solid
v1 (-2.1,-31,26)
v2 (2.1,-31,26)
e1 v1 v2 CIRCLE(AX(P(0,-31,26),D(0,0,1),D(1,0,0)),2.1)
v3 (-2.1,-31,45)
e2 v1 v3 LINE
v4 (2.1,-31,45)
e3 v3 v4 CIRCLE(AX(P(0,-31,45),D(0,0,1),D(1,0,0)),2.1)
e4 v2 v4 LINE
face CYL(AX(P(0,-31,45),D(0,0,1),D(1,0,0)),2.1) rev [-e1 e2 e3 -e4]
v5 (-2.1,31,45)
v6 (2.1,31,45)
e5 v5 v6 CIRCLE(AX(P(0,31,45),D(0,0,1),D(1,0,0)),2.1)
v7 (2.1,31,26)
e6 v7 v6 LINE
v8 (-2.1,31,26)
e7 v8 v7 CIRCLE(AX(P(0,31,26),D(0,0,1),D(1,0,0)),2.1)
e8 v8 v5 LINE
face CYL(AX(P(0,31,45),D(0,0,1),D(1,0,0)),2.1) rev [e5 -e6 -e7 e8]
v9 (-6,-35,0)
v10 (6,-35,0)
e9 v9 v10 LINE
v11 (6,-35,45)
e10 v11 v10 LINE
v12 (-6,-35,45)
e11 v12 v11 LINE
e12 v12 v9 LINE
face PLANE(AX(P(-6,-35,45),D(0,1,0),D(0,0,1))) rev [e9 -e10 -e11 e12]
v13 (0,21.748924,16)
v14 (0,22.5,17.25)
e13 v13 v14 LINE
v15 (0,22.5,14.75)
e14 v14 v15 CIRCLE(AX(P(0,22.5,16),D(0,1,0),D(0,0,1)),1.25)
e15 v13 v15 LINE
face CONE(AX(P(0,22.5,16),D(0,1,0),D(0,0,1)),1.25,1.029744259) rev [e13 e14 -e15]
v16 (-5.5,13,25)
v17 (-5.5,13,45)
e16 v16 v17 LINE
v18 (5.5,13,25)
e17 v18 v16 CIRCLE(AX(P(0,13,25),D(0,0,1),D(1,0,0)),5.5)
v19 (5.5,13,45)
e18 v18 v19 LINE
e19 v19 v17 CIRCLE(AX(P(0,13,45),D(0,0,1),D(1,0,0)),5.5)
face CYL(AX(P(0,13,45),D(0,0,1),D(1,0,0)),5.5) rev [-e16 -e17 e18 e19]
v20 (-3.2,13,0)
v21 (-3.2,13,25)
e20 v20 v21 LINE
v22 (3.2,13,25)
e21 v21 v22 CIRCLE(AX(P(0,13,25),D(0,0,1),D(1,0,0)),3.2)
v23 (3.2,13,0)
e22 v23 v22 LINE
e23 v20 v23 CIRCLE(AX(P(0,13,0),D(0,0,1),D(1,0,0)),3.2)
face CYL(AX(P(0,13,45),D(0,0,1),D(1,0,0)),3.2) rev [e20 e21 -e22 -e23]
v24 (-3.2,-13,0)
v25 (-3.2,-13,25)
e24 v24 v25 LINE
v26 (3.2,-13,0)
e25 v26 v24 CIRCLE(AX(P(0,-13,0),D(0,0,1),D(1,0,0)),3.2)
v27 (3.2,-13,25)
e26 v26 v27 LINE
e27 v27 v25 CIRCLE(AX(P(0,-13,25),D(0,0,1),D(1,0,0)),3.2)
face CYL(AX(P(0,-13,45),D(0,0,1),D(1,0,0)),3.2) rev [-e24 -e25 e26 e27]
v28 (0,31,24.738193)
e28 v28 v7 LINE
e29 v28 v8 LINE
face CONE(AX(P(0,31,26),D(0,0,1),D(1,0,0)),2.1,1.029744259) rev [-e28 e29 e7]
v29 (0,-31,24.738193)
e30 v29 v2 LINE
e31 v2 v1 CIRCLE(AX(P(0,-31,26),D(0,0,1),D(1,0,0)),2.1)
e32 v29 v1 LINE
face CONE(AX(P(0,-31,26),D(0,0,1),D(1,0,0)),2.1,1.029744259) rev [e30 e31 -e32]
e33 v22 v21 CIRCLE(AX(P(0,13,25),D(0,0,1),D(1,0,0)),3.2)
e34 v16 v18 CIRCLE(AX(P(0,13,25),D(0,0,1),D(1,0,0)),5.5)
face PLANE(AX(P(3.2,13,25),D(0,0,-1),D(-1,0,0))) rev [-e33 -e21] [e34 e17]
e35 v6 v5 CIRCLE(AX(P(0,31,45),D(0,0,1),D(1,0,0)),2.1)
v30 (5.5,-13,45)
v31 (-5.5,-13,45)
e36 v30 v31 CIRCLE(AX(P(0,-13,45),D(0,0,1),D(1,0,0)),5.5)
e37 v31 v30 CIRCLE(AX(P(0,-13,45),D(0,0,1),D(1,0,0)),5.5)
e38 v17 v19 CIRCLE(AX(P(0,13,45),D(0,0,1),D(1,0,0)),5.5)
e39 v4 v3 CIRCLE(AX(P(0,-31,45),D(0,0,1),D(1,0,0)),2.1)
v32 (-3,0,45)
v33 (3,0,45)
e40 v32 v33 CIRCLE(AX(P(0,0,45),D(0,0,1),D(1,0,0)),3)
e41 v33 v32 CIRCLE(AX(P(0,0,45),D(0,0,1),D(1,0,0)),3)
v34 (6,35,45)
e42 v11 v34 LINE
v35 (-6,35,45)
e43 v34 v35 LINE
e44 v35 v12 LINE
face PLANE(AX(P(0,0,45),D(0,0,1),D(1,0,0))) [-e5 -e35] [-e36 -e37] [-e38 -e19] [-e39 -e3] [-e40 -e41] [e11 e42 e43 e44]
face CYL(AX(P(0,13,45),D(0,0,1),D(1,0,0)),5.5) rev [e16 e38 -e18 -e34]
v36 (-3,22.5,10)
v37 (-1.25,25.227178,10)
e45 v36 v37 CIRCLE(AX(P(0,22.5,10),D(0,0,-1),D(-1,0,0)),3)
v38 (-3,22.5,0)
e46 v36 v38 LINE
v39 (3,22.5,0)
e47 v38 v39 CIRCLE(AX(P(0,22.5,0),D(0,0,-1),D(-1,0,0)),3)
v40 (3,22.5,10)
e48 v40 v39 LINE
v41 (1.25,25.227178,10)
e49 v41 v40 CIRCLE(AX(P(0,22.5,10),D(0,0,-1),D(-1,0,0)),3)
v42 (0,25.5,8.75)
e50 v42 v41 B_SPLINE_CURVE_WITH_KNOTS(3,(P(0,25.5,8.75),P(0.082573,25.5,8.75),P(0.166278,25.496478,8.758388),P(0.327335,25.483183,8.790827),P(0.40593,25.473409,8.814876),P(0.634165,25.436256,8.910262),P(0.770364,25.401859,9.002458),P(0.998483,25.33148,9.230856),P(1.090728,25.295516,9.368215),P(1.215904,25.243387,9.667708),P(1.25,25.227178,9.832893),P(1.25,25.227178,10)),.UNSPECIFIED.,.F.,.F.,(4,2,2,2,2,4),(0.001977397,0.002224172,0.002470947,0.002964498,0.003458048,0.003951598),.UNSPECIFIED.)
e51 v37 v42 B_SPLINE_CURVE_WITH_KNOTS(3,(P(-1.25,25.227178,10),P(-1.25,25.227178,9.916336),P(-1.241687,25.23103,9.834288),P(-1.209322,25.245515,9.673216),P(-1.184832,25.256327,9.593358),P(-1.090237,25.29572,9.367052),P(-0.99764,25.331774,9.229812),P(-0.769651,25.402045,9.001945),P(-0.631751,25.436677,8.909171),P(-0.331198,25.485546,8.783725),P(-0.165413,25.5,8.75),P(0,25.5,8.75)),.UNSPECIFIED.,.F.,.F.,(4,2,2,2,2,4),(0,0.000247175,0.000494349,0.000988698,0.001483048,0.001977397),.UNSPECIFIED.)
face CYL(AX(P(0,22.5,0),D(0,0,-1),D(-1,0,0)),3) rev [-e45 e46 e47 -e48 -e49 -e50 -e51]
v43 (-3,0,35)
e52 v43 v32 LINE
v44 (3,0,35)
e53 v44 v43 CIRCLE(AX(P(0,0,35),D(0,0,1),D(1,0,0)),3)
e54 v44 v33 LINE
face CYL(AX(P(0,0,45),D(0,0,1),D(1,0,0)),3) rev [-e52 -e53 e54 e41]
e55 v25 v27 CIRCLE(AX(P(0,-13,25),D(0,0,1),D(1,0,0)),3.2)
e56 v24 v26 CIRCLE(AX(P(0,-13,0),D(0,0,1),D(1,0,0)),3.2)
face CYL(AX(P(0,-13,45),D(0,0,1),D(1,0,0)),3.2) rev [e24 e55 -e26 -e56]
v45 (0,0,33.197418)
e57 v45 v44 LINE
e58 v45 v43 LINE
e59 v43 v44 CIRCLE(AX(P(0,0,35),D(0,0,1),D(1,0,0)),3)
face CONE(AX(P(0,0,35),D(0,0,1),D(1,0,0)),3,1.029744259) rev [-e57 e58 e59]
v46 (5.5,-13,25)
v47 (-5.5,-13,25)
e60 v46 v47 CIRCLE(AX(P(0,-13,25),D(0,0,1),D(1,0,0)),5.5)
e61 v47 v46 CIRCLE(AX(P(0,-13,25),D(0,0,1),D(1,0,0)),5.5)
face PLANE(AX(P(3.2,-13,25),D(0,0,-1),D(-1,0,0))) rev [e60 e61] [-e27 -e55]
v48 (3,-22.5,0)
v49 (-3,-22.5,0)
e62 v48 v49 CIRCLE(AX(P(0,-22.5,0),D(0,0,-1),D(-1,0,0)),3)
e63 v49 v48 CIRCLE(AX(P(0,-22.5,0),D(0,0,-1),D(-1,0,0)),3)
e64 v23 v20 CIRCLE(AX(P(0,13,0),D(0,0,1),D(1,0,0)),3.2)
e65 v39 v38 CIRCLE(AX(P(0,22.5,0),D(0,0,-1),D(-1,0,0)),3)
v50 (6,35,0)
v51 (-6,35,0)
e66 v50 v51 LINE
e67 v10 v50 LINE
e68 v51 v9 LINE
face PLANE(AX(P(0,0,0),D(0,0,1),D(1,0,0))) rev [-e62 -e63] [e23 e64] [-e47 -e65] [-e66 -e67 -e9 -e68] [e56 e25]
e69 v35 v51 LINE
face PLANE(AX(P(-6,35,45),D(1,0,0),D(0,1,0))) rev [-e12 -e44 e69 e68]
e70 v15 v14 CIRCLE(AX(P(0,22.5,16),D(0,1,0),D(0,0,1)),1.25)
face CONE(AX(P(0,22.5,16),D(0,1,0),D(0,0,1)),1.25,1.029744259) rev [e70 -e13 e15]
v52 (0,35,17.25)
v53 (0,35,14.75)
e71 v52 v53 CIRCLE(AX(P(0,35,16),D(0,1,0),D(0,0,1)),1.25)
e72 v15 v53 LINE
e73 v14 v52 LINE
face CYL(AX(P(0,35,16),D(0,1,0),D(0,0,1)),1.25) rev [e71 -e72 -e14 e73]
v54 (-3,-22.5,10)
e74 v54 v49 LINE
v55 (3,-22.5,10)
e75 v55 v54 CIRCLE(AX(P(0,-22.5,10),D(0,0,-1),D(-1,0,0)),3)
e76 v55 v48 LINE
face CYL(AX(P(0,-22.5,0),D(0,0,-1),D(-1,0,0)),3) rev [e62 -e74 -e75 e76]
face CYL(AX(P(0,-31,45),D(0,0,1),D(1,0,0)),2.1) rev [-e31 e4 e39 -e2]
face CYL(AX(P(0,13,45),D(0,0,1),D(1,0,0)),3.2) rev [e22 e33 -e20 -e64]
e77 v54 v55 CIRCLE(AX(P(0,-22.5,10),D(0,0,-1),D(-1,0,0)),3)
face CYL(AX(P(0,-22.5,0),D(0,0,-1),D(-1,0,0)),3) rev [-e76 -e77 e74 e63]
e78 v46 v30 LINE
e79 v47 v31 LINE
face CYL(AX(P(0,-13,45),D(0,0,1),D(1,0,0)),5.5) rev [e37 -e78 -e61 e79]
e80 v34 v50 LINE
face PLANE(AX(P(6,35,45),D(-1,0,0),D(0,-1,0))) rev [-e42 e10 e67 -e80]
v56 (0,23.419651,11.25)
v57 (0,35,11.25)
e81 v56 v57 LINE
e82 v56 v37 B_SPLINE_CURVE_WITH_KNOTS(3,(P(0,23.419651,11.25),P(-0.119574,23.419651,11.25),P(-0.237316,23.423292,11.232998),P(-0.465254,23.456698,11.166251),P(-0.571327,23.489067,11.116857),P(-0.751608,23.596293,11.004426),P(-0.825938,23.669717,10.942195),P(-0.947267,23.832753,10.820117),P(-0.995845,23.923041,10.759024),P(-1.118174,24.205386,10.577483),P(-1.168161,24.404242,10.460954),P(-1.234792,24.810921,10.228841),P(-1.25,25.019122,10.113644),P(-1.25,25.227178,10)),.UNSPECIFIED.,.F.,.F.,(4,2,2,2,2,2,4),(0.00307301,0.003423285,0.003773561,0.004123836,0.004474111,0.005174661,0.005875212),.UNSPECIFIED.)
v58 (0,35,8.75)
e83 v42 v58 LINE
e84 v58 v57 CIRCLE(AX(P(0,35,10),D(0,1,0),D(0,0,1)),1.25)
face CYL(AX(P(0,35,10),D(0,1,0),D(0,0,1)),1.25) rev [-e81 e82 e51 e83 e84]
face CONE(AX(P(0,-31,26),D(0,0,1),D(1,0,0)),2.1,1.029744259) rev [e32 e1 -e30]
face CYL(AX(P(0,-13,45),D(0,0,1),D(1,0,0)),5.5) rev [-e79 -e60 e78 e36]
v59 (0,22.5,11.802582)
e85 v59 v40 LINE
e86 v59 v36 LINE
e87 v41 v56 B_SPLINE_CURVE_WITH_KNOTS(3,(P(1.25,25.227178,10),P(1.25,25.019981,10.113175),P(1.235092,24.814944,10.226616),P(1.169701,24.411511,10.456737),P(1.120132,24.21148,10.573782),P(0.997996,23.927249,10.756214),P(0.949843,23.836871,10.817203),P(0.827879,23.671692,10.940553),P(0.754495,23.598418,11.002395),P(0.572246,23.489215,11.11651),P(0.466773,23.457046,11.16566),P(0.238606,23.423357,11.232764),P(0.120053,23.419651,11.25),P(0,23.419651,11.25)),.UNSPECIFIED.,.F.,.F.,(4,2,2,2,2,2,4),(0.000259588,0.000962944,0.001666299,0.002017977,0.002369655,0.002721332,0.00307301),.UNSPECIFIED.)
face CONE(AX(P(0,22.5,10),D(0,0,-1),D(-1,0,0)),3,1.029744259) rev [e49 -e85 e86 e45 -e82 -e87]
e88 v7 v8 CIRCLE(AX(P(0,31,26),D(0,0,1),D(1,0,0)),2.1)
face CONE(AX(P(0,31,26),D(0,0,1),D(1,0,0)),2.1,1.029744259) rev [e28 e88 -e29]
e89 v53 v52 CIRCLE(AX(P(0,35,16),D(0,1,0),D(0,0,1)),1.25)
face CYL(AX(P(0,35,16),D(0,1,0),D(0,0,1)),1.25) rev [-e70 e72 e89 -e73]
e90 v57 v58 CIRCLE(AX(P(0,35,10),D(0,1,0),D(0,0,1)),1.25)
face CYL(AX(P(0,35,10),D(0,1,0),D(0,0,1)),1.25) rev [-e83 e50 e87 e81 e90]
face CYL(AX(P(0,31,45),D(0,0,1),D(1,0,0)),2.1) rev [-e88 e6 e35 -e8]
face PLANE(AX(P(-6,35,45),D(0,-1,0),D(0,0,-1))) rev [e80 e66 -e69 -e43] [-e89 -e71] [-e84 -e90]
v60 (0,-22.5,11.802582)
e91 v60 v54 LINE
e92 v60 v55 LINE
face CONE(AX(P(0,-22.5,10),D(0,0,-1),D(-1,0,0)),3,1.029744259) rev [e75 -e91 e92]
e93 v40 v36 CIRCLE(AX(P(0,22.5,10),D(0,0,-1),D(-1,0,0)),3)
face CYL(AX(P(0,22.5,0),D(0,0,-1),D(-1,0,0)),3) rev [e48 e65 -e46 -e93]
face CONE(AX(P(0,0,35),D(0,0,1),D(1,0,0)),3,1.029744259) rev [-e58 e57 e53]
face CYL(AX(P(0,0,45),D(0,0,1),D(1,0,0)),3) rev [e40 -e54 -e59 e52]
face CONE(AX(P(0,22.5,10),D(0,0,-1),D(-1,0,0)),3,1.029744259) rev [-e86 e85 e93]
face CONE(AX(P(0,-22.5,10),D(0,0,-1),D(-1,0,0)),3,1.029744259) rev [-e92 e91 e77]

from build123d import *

# Parameters (mm, degrees)
SKETCH_13_W               = 12
SKETCH_13_H               = 70
EXTRUDE_1_DEPTH           = 45
HOLE_WIZARD_M3_1_D        = 2.5
HOLE_WIZARD_M3_1_DEPTH    = 12.5
HOLE_WIZARD_M3_1_TIP      = 0.751075774
HOLE_WIZARD_M5_1_D        = 4.2
HOLE_WIZARD_M5_1_DEPTH    = 19
HOLE_WIZARD_M5_1_TIP      = 1.2618073
HOLE_WIZARD_1_D           = 6.4
HOLE_WIZARD_1_CBORE_D     = 11
HOLE_WIZARD_1_CBORE_DEPTH = 20
HOLE_WIZARD_6_0_6_1_D     = 6
HOLE_WIZARD_6_0_6_1_DEPTH = 10
HOLE_WIZARD_6_0_6_1_TIP   = 1.802581857
HOLE_WIZARD_6_0_6_2_D     = 6
HOLE_WIZARD_6_0_6_2_DEPTH = 10
HOLE_WIZARD_6_0_6_2_TIP   = 1.802581857


with BuildPart() as part:
    # 草图13 → 凸台-拉伸1 (new body)
    with BuildSketch(Plane.XY):
        Rectangle(SKETCH_13_W, SKETCH_13_H)
    extrude(amount=EXTRUDE_1_DEPTH)

    # M3 螺纹孔1
    with Locations(Plane(origin=(0, 35, 0), x_dir=(1, 0, 0), z_dir=(0, 1, 0))):
        with Locations((0, -10), (0, -16)):
            Hole(HOLE_WIZARD_M3_1_D / 2, depth=HOLE_WIZARD_M3_1_DEPTH)
            with Locations((0, 0, -(HOLE_WIZARD_M3_1_DEPTH + HOLE_WIZARD_M3_1_TIP / 2))):  # 118° drill point
                Cone(0, HOLE_WIZARD_M3_1_D / 2, HOLE_WIZARD_M3_1_TIP, mode=Mode.SUBTRACT)

    # M5 螺纹孔1
    with Locations(Plane.XY.offset(45)):
        with Locations((0, 31), (0, -31)):
            Hole(HOLE_WIZARD_M5_1_D / 2, depth=HOLE_WIZARD_M5_1_DEPTH)
            with Locations((0, 0, -(HOLE_WIZARD_M5_1_DEPTH + HOLE_WIZARD_M5_1_TIP / 2))):  # 118° drill point
                Cone(0, HOLE_WIZARD_M5_1_D / 2, HOLE_WIZARD_M5_1_TIP, mode=Mode.SUBTRACT)

    # 打孔尺寸(%根据)内六角圆柱头螺钉的类型1 (through all)
    with Locations(Plane.XY.offset(45)):
        with Locations((0, 13), (0, -13)):
            CounterBoreHole(HOLE_WIZARD_1_D / 2, HOLE_WIZARD_1_CBORE_D / 2, HOLE_WIZARD_1_CBORE_DEPTH)

    # Ø6.0 (6) 直径孔1
    with Locations(Plane.XY.offset(45)):
        with Locations((0, 0)):
            Hole(HOLE_WIZARD_6_0_6_1_D / 2, depth=HOLE_WIZARD_6_0_6_1_DEPTH)
            with Locations((0, 0, -(HOLE_WIZARD_6_0_6_1_DEPTH + HOLE_WIZARD_6_0_6_1_TIP / 2))):  # 118° drill point
                Cone(0, HOLE_WIZARD_6_0_6_1_D / 2, HOLE_WIZARD_6_0_6_1_TIP, mode=Mode.SUBTRACT)

    # Ø6.0 (6) 直径孔2
    with Locations(Plane(origin=(0, 0, 0), x_dir=(-1, 0, 0), z_dir=(0, 0, -1))):
        with Locations((0, -22.5), (0, 22.5)):
            Hole(HOLE_WIZARD_6_0_6_2_D / 2, depth=HOLE_WIZARD_6_0_6_2_DEPTH)
            with Locations((0, 0, -(HOLE_WIZARD_6_0_6_2_DEPTH + HOLE_WIZARD_6_0_6_2_TIP / 2))):  # 118° drill point
                Cone(0, HOLE_WIZARD_6_0_6_2_D / 2, HOLE_WIZARD_6_0_6_2_TIP, mode=Mode.SUBTRACT)


solid = part.part
